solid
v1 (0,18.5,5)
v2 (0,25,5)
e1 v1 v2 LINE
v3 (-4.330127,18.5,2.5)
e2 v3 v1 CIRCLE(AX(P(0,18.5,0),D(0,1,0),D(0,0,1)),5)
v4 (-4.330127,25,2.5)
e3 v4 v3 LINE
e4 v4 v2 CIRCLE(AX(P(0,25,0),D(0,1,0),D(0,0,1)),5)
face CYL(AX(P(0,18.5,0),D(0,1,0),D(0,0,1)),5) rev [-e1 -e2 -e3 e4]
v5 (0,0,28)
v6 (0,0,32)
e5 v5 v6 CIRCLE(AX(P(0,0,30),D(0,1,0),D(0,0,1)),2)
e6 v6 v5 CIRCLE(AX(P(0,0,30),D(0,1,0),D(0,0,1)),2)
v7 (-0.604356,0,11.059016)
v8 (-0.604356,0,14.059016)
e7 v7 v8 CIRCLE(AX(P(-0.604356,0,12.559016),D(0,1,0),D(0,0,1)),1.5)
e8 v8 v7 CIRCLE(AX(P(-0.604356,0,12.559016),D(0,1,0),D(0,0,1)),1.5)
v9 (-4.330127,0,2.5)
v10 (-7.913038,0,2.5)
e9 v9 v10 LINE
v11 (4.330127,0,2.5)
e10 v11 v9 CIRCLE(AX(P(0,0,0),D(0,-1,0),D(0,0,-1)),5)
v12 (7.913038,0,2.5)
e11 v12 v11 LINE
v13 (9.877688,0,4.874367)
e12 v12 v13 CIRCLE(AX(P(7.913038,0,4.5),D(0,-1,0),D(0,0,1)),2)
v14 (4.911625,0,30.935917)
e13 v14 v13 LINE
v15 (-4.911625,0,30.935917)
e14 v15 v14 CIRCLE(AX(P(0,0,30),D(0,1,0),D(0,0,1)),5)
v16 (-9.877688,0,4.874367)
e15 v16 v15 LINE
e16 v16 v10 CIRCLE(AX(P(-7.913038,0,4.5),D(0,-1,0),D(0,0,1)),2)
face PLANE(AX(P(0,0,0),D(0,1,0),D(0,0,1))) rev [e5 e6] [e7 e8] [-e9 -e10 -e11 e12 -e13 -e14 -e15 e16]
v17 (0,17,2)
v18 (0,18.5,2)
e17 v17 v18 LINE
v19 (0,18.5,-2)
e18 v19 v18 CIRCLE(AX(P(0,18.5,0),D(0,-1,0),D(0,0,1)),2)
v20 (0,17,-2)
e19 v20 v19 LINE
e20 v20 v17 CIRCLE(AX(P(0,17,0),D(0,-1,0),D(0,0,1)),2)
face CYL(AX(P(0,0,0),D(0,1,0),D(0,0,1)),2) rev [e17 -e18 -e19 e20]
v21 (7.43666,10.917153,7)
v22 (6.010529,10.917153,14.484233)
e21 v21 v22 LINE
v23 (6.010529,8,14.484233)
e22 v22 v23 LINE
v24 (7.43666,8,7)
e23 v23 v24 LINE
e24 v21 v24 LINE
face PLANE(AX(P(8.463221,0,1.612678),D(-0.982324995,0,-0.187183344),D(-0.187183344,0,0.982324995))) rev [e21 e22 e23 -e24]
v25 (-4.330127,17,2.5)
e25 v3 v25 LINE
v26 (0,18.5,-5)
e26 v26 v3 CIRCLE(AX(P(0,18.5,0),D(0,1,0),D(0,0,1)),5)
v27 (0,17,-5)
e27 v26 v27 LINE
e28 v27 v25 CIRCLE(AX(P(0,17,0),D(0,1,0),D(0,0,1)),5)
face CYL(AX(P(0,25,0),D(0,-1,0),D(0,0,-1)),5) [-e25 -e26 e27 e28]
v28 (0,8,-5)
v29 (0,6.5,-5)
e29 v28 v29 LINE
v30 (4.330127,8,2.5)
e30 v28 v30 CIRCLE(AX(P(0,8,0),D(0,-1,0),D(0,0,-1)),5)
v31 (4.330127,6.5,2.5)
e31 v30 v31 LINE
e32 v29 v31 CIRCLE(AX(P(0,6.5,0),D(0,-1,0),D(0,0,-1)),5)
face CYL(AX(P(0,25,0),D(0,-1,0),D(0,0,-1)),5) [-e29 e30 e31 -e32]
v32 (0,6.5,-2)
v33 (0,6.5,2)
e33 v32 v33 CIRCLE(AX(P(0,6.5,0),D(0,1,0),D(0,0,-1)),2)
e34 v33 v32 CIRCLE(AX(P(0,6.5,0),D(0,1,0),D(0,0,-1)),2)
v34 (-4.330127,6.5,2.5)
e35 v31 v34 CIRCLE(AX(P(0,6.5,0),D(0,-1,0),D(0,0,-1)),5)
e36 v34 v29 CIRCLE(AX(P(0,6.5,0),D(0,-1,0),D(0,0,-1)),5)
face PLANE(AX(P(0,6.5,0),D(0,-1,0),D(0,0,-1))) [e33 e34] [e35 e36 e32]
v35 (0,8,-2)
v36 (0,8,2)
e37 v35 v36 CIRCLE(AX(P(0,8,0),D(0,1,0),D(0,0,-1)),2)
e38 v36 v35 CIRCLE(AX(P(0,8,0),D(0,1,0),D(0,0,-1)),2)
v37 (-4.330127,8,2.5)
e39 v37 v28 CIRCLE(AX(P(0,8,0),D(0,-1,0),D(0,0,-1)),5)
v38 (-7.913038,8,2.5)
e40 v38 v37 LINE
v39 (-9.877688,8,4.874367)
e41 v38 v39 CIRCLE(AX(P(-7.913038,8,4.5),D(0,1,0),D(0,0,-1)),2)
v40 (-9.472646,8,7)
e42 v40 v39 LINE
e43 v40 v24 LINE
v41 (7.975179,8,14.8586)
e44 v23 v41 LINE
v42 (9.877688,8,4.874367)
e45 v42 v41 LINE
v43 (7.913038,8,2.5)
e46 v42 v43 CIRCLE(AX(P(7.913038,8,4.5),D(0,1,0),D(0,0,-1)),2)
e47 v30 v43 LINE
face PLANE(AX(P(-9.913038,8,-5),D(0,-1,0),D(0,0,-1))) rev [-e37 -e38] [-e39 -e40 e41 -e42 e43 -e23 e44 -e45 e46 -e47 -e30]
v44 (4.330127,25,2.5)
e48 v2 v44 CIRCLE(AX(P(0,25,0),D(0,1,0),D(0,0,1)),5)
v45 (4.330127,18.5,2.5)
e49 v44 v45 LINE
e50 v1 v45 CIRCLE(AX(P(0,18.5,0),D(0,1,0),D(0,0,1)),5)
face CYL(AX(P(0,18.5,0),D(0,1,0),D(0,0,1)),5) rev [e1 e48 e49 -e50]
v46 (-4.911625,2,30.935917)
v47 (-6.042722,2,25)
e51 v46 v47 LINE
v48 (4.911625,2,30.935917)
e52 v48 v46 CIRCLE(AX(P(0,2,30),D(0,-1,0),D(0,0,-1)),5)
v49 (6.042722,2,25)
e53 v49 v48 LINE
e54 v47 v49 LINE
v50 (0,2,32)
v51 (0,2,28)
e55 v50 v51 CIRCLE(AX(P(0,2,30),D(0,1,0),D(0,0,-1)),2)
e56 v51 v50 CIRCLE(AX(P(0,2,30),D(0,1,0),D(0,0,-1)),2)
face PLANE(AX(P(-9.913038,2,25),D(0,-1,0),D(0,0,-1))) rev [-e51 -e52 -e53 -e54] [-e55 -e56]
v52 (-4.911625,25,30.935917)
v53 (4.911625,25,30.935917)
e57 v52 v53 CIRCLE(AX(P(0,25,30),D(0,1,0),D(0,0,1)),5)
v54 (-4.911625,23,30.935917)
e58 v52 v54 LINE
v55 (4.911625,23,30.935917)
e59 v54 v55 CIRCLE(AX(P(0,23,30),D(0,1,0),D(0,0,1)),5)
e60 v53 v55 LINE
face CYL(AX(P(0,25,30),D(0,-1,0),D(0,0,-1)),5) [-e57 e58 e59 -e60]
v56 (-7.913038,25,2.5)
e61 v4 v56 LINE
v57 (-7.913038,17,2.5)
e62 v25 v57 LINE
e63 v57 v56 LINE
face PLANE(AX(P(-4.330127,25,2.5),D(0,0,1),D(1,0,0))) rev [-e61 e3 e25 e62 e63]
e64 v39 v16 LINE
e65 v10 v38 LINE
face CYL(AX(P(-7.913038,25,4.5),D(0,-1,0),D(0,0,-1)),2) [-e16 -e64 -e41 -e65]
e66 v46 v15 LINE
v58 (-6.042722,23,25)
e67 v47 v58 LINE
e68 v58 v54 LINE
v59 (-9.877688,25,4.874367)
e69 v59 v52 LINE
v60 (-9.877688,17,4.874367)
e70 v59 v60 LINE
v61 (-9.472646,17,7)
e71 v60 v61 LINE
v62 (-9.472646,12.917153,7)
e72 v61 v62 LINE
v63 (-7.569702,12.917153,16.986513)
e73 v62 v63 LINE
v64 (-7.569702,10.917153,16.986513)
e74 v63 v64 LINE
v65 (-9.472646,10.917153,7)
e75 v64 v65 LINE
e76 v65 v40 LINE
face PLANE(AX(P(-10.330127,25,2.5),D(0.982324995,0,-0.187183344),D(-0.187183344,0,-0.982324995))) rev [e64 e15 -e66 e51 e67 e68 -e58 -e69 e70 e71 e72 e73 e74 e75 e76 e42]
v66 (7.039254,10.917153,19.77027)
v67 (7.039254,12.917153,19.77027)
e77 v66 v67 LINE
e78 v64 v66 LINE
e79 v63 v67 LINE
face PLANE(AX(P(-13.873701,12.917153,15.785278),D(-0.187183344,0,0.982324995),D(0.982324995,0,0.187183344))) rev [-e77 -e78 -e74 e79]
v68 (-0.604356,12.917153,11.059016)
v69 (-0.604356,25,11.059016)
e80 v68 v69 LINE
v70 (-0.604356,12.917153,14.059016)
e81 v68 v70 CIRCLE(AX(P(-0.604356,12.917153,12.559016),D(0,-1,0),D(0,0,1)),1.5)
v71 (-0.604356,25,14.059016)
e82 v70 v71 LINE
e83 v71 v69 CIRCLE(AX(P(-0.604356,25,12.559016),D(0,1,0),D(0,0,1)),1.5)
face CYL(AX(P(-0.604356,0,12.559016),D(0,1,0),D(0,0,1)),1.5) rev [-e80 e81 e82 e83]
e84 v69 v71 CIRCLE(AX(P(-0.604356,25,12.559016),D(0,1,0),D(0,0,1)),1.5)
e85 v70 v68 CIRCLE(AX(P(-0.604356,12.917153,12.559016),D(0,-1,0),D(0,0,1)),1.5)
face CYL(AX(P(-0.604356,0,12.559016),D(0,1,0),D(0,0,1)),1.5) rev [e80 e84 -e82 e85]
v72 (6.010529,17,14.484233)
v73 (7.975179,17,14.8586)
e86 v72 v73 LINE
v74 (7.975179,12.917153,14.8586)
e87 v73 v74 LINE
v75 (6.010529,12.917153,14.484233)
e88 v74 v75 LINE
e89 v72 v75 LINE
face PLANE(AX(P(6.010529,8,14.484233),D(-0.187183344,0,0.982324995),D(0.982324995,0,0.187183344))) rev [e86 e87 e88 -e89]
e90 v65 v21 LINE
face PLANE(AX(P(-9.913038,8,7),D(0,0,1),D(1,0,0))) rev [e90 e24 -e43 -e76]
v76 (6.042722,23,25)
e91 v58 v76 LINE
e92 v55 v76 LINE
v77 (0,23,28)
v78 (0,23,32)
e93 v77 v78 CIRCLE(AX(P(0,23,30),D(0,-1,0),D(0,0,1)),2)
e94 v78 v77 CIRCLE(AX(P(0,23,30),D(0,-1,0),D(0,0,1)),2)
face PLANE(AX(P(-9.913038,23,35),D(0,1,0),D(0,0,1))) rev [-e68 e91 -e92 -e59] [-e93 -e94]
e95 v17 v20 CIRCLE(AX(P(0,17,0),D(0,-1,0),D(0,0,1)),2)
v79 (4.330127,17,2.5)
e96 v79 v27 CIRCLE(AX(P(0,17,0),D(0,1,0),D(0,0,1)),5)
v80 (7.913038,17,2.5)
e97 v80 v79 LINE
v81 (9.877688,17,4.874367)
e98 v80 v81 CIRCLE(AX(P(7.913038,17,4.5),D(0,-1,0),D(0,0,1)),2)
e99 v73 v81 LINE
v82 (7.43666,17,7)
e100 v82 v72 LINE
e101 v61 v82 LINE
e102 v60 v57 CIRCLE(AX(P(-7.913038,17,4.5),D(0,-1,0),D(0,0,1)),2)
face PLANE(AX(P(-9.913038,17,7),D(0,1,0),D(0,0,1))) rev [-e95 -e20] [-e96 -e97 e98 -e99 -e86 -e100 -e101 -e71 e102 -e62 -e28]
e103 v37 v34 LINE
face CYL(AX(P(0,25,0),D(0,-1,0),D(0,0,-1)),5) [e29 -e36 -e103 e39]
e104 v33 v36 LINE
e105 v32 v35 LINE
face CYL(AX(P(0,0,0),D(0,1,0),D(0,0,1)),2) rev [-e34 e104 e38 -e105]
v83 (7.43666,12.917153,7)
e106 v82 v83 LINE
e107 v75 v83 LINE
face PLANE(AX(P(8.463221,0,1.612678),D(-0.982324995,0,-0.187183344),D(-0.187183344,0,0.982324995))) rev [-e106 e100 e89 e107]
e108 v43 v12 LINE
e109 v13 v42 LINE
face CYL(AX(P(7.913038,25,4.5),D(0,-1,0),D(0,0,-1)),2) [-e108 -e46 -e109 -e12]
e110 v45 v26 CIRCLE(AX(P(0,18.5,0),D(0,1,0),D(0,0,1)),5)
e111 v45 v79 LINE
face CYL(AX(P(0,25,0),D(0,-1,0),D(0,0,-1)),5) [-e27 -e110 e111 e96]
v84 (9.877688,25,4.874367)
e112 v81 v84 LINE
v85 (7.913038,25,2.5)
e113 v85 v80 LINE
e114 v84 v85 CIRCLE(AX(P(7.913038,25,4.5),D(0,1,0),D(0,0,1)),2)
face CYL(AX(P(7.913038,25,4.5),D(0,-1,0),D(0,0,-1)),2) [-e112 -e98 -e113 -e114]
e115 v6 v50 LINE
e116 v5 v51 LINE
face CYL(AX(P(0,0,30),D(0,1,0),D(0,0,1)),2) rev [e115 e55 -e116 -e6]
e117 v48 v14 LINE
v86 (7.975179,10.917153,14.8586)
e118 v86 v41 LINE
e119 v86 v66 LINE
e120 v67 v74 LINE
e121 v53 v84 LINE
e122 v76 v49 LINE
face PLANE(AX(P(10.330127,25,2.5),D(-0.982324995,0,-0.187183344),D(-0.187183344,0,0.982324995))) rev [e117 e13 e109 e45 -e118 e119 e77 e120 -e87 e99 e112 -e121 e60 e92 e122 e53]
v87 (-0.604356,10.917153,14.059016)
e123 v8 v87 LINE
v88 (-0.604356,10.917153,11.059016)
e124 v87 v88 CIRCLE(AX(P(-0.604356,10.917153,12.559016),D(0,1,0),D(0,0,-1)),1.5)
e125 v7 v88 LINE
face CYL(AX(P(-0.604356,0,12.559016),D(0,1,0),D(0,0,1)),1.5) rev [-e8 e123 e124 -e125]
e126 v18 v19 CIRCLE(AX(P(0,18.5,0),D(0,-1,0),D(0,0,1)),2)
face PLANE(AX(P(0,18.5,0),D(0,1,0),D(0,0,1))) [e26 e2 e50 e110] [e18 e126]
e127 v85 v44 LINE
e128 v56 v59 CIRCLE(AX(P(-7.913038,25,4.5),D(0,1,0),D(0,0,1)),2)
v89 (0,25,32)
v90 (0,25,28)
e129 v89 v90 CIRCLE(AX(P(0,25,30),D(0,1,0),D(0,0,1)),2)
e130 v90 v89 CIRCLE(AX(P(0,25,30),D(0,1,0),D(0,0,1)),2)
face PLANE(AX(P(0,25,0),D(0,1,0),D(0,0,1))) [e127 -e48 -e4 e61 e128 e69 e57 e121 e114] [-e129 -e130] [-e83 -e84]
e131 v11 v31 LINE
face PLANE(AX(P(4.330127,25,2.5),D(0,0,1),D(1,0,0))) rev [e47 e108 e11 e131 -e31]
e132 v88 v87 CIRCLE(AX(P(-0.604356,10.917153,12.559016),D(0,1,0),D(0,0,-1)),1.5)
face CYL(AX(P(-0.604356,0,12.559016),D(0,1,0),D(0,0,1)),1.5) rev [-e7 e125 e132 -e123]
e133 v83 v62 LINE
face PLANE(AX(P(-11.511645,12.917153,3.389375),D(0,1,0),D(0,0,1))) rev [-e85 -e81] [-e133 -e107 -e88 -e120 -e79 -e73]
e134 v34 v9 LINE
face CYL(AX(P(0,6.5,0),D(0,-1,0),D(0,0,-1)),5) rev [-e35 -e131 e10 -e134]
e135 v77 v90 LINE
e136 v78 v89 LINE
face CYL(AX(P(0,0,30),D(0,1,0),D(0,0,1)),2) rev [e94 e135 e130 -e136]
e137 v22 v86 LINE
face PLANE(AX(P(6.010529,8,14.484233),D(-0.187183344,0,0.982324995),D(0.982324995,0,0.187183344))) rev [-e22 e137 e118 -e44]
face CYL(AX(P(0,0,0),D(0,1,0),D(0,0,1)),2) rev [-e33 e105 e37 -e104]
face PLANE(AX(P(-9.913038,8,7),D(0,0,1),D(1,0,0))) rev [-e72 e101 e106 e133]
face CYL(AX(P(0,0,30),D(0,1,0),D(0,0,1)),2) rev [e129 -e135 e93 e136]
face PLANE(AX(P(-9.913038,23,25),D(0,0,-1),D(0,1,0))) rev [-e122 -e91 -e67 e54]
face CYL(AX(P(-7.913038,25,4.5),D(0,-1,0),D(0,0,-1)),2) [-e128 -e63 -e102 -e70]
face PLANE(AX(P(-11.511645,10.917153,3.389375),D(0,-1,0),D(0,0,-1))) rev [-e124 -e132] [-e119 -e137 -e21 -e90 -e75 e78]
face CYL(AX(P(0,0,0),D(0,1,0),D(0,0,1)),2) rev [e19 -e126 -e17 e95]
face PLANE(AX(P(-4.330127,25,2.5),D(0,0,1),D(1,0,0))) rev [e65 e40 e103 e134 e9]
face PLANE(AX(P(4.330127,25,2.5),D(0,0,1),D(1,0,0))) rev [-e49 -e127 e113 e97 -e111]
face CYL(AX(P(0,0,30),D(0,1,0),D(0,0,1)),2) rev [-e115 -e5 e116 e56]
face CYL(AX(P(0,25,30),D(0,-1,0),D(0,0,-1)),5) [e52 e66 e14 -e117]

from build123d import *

# Parameters (mm, degrees)
BOSS_EXTRUDE1_DEPTH     = 25
SKETCH2_R               = 2
CUT_EXTRUDE1_DEPTH      = 45.234732103
FILLET1_R               = 2
FILLET2_R               = 2
CUT_EXTRUDE2_START      = -6.5
SKETCH3_R               = 5
CUT_EXTRUDE2_DEPTH      = 6.5
SKETCH4_R               = 5
CUT_EXTRUDE3_DEPTH      = 6.5
CUT_EXTRUDE4_DEPTH      = 45.13919265
CUT_EXTRUDE4_DEPTH_BACK = 45.13919265
SKETCH5_W               = 10
SKETCH5_H               = 21
SKETCH5_W_2             = 12
SKETCH5_H_2             = 9
SKETCH7_W               = 8
SKETCH7_H               = 9
CUT_EXTRUDE5_DEPTH      = 2
CUT_EXTRUDE6_DEPTH      = 189.558524252
CUT_EXTRUDE6_DEPTH_BACK = 189.558524252
SKETCH8_R               = 1.5
CUT_EXTRUDE7_DEPTH      = 46.578505635
CUT_EXTRUDE7_DEPTH_BACK = 46.578505635
SKETCH9_W               = 12.618942776
SKETCH9_H               = 2


with BuildPart() as part:
    # Sketch1 → Boss-Extrude1 (new body)
    with BuildSketch(Plane(origin=(0, 0, 0), x_dir=(1, 0, 0), z_dir=(0, 1, 0))):
        with BuildLine():
            Line((-4.330127019, -2.5), (-10.330127019, -2.5))
            Line((-10.330127019, -2.5), (-4.911624974, -30.935916722))
            ThreePointArc((-4.911624974, -30.935916722), (0, -35), (4.911624974, -30.935916722))
            Line((4.911624974, -30.935916722), (10.330127019, -2.5))
            Line((10.330127019, -2.5), (4.330127019, -2.5))
            ThreePointArc((4.330127019, -2.5), (0, 5), (-4.330127019, -2.5))
        make_face()
    extrude(amount=BOSS_EXTRUDE1_DEPTH)

    # Sketch2 → Cut-Extrude1 (cut, through all)
    with BuildSketch(Plane(origin=(0, 25, 0), x_dir=(1, 0, 0), z_dir=(0, 1, 0))):
        with Locations(Location((0, 0, 0), (0, 0, 270))):
            Circle(SKETCH2_R)
        with Locations(Location((0, -30, 0), (0, 0, 270))):
            Circle(SKETCH2_R)
    extrude(amount=-CUT_EXTRUDE1_DEPTH, mode=Mode.SUBTRACT)

    # Fillet1
    fillet1_edges = [part.edges().sort_by_distance(p)[0] for p in [
        (10.330127019, 12.5, 2.5),
    ]]
    fillet(fillet1_edges, radius=FILLET1_R)

    # Fillet2
    fillet2_edges = [part.edges().sort_by_distance(p)[0] for p in [
        (-10.330127019, 12.5, 2.5),
    ]]
    fillet(fillet2_edges, radius=FILLET2_R)

    # Sketch3 → Cut-Extrude2 (cut)
    with BuildSketch(Plane(origin=(0, 25, 0), x_dir=(1, 0, 0), z_dir=(0, 1, 0)).offset(CUT_EXTRUDE2_START)):
        Circle(SKETCH3_R)
    extrude(amount=CUT_EXTRUDE2_DEPTH, mode=Mode.SUBTRACT)

    # Sketch4 → Cut-Extrude3 (cut)
    with BuildSketch(Plane.XZ):
        Circle(SKETCH4_R)
    extrude(amount=-CUT_EXTRUDE3_DEPTH, mode=Mode.SUBTRACT)

    # Sketch5 → Cut-Extrude4 (cut, two sides: drawn at the far end of the back side and taken through both)
    with BuildSketch(Plane(origin=(0, 0, 0), x_dir=(0, 0, -1), z_dir=(1, 0, 0)).offset(-CUT_EXTRUDE4_DEPTH_BACK)):
        with Locations((-30, 12.5)):
            Rectangle(SKETCH5_W, SKETCH5_H)
        with Locations((-1, 12.5)):
            Rectangle(SKETCH5_W_2, SKETCH5_H_2)
    extrude(amount=CUT_EXTRUDE4_DEPTH + CUT_EXTRUDE4_DEPTH_BACK, mode=Mode.SUBTRACT)

    # Sketch7 → Cut-Extrude5 (cut)
    with BuildSketch(Plane(origin=(10.427871309, 0, 1.987044855), x_dir=(0.18718334440142867, 0, -0.9823249948864665), z_dir=(0.9823249948864665, 0, 0.18718334440142867))):
        with Locations((-9.103153408, 12.5)):
            Rectangle(SKETCH7_W, SKETCH7_H)
    extrude(amount=-CUT_EXTRUDE5_DEPTH, mode=Mode.SUBTRACT)

    # Sketch8 → Cut-Extrude6 (cut, two sides: drawn at the far end of the back side and taken through both)
    with BuildSketch(Plane(origin=(59.598686513, 25, -138.486129663), x_dir=(0.989316462347077, 0, 0.14578387197857126), z_dir=(0, 1, 0)).offset(-CUT_EXTRUDE6_DEPTH_BACK)):
        with Locations(Location((-37.539914968, -158.208081577, 0), (0, 0, 278.382674106))):
            Circle(SKETCH8_R)
    extrude(amount=CUT_EXTRUDE6_DEPTH + CUT_EXTRUDE6_DEPTH_BACK, mode=Mode.SUBTRACT)

    # Sketch9 → Cut-Extrude7 (cut, two sides: drawn at the far end of the back side and taken through both)
    with BuildSketch(Plane(origin=(8.46322132, 0, 1.612678166), x_dir=(0.18718334440142864, 0, -0.9823249948864664), z_dir=(0.9823249948864664, 0, 0.18718334440142864)).offset(-CUT_EXTRUDE7_DEPTH_BACK)):
        with Locations((-11.793727477, 11.917152734)):
            Rectangle(SKETCH9_W, SKETCH9_H)
    extrude(amount=CUT_EXTRUDE7_DEPTH + CUT_EXTRUDE7_DEPTH_BACK, mode=Mode.SUBTRACT)


solid = part.part
